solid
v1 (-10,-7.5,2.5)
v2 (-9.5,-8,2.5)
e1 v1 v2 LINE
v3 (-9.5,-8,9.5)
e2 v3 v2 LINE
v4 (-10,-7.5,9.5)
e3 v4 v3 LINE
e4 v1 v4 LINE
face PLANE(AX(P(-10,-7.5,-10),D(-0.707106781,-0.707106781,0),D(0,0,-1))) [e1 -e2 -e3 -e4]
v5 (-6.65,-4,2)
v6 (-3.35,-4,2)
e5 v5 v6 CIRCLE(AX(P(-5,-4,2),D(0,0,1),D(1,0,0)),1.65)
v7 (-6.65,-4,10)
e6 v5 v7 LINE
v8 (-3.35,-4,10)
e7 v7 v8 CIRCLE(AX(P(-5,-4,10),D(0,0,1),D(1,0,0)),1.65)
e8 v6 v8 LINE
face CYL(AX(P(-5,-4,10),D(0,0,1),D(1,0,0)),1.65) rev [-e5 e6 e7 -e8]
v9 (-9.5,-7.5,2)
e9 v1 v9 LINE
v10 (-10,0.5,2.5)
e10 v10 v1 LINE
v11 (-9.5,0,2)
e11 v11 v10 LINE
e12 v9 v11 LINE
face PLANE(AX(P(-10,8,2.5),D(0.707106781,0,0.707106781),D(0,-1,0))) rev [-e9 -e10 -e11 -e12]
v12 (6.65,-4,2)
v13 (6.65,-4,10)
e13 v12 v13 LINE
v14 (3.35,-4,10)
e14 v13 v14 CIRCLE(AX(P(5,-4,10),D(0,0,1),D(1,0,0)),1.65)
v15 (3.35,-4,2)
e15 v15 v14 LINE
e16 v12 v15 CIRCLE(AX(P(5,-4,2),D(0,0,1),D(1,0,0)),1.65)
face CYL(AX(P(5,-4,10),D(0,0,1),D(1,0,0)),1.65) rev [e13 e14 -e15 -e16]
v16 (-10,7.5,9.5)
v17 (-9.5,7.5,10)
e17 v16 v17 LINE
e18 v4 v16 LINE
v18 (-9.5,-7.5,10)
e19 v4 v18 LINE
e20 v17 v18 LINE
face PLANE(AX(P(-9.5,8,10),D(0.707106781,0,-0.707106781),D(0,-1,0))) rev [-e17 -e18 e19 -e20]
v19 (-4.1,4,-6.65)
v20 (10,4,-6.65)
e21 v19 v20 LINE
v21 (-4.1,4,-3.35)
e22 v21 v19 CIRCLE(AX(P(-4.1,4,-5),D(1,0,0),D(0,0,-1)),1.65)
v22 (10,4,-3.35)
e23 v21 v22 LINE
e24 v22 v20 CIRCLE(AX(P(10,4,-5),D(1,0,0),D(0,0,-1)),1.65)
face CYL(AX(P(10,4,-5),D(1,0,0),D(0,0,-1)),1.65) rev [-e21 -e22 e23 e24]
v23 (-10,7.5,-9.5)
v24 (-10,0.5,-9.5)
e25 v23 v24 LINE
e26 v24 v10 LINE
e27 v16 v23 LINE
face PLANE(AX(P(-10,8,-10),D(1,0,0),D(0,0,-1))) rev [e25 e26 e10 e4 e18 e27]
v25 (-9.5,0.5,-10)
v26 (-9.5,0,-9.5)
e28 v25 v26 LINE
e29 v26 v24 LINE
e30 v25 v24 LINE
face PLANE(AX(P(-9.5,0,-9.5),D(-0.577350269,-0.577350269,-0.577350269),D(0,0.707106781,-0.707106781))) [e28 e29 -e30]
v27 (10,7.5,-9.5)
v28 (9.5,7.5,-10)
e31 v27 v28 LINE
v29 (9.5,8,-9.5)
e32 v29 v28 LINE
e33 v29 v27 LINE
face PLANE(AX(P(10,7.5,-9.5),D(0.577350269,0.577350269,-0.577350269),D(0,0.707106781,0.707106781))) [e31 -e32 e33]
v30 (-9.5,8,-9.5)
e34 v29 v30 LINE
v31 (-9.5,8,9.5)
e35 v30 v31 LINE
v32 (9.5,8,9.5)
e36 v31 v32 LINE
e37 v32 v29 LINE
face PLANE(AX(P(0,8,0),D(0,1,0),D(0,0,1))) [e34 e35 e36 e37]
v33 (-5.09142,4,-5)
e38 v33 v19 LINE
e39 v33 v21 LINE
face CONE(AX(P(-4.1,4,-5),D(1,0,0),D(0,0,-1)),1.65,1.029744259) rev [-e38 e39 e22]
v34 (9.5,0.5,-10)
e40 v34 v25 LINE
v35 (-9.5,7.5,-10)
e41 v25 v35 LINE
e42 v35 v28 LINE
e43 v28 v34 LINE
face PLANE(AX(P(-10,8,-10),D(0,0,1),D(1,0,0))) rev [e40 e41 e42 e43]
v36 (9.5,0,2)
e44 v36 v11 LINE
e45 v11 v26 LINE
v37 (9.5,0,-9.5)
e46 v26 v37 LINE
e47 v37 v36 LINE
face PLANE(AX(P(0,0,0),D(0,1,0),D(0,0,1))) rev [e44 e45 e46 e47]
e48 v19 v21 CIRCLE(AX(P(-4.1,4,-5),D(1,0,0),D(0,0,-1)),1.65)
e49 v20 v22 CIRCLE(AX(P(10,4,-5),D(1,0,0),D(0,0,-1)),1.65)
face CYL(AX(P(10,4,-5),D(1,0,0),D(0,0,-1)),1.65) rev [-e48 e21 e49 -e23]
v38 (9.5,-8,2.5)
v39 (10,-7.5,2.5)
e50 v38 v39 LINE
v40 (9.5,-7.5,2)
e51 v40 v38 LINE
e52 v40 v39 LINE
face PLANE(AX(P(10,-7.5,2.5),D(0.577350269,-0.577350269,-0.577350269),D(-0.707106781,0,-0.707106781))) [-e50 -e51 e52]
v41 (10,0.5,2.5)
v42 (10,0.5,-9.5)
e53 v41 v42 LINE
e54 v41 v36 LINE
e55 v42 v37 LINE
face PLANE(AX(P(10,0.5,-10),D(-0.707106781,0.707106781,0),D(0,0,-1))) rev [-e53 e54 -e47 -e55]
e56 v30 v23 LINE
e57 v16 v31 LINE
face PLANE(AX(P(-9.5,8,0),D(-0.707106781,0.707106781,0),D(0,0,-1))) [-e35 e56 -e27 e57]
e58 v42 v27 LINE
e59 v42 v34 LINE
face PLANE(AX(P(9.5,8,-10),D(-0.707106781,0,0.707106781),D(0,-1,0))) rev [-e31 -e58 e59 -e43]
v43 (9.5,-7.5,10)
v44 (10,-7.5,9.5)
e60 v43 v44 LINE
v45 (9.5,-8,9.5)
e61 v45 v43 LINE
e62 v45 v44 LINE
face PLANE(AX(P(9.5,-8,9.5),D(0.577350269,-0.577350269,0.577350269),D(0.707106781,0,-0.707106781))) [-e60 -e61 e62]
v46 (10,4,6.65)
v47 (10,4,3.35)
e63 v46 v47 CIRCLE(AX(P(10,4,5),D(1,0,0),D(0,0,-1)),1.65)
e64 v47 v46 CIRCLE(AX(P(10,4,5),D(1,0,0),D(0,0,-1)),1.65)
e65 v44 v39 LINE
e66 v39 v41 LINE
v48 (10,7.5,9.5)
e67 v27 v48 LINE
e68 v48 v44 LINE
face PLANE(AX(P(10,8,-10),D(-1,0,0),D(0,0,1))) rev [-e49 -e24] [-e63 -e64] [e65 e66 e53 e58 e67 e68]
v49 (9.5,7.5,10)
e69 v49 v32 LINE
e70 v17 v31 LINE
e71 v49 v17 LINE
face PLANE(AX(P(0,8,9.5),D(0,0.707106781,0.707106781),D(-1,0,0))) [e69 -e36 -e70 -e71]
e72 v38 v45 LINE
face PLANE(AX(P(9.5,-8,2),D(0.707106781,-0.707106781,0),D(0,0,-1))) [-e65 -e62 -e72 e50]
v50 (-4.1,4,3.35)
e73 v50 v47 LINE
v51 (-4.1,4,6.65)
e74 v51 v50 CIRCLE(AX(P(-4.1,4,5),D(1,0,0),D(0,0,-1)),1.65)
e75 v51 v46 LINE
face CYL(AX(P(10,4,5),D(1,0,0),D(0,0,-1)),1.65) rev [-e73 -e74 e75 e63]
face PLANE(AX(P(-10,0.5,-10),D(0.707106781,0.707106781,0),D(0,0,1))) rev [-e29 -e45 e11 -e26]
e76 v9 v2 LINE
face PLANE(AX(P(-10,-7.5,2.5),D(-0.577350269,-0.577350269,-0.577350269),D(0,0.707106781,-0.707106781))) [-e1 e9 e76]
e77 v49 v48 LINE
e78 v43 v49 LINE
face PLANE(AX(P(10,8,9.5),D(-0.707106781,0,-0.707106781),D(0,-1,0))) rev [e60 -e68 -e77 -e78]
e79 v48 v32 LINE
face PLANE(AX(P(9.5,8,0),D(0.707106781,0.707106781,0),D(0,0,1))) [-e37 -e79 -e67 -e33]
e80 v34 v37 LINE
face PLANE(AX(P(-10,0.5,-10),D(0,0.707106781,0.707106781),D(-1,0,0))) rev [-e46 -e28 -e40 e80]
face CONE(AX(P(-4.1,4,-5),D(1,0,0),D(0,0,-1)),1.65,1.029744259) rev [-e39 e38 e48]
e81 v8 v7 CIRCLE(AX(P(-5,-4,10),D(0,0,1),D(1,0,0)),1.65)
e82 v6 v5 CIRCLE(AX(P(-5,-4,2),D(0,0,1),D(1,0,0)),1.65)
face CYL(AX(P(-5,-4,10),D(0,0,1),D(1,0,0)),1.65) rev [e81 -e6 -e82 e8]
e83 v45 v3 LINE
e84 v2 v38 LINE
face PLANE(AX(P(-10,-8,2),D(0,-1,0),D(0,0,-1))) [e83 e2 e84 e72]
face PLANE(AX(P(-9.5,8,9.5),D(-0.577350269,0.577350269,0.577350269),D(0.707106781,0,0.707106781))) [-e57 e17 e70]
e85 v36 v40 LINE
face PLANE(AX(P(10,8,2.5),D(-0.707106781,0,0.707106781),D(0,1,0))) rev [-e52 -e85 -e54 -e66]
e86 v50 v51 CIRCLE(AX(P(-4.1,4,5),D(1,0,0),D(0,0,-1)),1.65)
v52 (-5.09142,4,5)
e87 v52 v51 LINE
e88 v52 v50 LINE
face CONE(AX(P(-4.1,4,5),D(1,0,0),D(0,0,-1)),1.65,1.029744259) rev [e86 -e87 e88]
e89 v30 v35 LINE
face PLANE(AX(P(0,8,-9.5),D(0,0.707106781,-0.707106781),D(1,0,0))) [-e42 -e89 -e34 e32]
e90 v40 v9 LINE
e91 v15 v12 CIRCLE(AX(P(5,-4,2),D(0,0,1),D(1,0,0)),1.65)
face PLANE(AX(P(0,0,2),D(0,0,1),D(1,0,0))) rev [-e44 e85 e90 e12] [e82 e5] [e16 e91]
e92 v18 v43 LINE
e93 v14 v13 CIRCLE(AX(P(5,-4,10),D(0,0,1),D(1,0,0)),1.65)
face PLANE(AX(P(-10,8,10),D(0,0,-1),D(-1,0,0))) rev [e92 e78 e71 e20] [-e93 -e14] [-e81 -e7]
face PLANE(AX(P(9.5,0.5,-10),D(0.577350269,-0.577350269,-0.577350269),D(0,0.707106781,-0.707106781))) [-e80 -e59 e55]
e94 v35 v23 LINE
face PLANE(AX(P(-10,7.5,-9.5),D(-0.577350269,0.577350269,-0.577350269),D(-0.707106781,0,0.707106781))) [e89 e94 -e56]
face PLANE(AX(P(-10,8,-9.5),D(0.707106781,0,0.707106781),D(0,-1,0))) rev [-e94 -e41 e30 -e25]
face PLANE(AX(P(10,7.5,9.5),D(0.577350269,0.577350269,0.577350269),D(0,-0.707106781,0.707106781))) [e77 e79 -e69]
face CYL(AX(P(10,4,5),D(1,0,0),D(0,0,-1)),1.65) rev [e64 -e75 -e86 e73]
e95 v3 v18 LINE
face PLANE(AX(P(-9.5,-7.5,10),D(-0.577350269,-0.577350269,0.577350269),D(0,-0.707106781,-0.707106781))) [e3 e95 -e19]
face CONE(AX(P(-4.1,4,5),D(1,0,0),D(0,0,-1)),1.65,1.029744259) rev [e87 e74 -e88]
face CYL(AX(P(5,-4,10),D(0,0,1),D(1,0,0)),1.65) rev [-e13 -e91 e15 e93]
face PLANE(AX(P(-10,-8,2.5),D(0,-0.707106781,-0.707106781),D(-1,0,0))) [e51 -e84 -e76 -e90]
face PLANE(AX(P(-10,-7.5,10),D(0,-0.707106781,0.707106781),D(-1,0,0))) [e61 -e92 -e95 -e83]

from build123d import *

# Parameters (mm, degrees)
SKETCH_1_W             = 20
SKETCH_1_H             = 20
EXTRUDE_1_DEPTH        = 8
HOLE_WIZARD_M4_1_D     = 3.3
HOLE_WIZARD_M4_1_DEPTH = 14.1
HOLE_WIZARD_M4_1_TIP   = 0.991420021
SKETCH_6_W             = 20
SKETCH_6_H             = 8
EXTRUDE_2_DEPTH        = 8
HOLE_WIZARD_M4_3_D     = 3.3
HOLE_WIZARD_M4_3_DEPTH = 14.1
HOLE_WIZARD_M4_3_TIP   = 0.991420021
CHAMFER_2_SIZE         = 0.5


with BuildPart() as part:
    # 草图1 → 凸台-拉伸1 (new body)
    with BuildSketch(Plane(origin=(0, 0, 0), x_dir=(1, 0, 0), z_dir=(0, 1, 0))):
        Rectangle(SKETCH_1_W, SKETCH_1_H)
    extrude(amount=EXTRUDE_1_DEPTH)

    # M4 螺纹孔1
    with Locations(Plane(origin=(10, 0, 0), x_dir=(0, 0, -1), z_dir=(1, 0, 0))):
        with Locations((5, 4), (-5, 4)):
            Hole(HOLE_WIZARD_M4_1_D / 2, depth=HOLE_WIZARD_M4_1_DEPTH)
            with Locations((0, 0, -(HOLE_WIZARD_M4_1_DEPTH + HOLE_WIZARD_M4_1_TIP / 2))):  # 118° drill point
                Cone(0, HOLE_WIZARD_M4_1_D / 2, HOLE_WIZARD_M4_1_TIP, mode=Mode.SUBTRACT)

    # 草图6 → 凸台-拉伸2 (add)
    with BuildSketch(Plane.XY.offset(10)):
        with Locations((0, -4)):
            Rectangle(SKETCH_6_W, SKETCH_6_H)
    extrude(amount=-EXTRUDE_2_DEPTH)

    # M4 螺纹孔3
    with Locations(Plane.XY.offset(10)):
        with Locations((-5, -4), (5, -4)):
            Hole(HOLE_WIZARD_M4_3_D / 2, depth=HOLE_WIZARD_M4_3_DEPTH)
            with Locations((0, 0, -(HOLE_WIZARD_M4_3_DEPTH + HOLE_WIZARD_M4_3_TIP / 2))):  # 118° drill point
                Cone(0, HOLE_WIZARD_M4_3_D / 2, HOLE_WIZARD_M4_3_TIP, mode=Mode.SUBTRACT)

    # 倒角2
    chamfer_2_edges = [part.edges().sort_by_distance(p)[0] for p in [
        (-10, 8, 0),
        (-10, 0, 10),
        (-10, -4, 2),
        (-10, 0, -4),
        (10, 4, -10),
        (0, 8, -10),
        (-10, 4, -10),
        (0, 0, -10),
        (10, -8, 6),
        (10, 0, -4),
        (10, -4, 2),
        (0, -8, 2),
        (-10, -8, 6),
        (0, -8, 10),
        (10, 8, 0),
        (0, 8, 10),
        (10, 0, 10),
    ]]
    chamfer(chamfer_2_edges, length=CHAMFER_2_SIZE)


solid = part.part
